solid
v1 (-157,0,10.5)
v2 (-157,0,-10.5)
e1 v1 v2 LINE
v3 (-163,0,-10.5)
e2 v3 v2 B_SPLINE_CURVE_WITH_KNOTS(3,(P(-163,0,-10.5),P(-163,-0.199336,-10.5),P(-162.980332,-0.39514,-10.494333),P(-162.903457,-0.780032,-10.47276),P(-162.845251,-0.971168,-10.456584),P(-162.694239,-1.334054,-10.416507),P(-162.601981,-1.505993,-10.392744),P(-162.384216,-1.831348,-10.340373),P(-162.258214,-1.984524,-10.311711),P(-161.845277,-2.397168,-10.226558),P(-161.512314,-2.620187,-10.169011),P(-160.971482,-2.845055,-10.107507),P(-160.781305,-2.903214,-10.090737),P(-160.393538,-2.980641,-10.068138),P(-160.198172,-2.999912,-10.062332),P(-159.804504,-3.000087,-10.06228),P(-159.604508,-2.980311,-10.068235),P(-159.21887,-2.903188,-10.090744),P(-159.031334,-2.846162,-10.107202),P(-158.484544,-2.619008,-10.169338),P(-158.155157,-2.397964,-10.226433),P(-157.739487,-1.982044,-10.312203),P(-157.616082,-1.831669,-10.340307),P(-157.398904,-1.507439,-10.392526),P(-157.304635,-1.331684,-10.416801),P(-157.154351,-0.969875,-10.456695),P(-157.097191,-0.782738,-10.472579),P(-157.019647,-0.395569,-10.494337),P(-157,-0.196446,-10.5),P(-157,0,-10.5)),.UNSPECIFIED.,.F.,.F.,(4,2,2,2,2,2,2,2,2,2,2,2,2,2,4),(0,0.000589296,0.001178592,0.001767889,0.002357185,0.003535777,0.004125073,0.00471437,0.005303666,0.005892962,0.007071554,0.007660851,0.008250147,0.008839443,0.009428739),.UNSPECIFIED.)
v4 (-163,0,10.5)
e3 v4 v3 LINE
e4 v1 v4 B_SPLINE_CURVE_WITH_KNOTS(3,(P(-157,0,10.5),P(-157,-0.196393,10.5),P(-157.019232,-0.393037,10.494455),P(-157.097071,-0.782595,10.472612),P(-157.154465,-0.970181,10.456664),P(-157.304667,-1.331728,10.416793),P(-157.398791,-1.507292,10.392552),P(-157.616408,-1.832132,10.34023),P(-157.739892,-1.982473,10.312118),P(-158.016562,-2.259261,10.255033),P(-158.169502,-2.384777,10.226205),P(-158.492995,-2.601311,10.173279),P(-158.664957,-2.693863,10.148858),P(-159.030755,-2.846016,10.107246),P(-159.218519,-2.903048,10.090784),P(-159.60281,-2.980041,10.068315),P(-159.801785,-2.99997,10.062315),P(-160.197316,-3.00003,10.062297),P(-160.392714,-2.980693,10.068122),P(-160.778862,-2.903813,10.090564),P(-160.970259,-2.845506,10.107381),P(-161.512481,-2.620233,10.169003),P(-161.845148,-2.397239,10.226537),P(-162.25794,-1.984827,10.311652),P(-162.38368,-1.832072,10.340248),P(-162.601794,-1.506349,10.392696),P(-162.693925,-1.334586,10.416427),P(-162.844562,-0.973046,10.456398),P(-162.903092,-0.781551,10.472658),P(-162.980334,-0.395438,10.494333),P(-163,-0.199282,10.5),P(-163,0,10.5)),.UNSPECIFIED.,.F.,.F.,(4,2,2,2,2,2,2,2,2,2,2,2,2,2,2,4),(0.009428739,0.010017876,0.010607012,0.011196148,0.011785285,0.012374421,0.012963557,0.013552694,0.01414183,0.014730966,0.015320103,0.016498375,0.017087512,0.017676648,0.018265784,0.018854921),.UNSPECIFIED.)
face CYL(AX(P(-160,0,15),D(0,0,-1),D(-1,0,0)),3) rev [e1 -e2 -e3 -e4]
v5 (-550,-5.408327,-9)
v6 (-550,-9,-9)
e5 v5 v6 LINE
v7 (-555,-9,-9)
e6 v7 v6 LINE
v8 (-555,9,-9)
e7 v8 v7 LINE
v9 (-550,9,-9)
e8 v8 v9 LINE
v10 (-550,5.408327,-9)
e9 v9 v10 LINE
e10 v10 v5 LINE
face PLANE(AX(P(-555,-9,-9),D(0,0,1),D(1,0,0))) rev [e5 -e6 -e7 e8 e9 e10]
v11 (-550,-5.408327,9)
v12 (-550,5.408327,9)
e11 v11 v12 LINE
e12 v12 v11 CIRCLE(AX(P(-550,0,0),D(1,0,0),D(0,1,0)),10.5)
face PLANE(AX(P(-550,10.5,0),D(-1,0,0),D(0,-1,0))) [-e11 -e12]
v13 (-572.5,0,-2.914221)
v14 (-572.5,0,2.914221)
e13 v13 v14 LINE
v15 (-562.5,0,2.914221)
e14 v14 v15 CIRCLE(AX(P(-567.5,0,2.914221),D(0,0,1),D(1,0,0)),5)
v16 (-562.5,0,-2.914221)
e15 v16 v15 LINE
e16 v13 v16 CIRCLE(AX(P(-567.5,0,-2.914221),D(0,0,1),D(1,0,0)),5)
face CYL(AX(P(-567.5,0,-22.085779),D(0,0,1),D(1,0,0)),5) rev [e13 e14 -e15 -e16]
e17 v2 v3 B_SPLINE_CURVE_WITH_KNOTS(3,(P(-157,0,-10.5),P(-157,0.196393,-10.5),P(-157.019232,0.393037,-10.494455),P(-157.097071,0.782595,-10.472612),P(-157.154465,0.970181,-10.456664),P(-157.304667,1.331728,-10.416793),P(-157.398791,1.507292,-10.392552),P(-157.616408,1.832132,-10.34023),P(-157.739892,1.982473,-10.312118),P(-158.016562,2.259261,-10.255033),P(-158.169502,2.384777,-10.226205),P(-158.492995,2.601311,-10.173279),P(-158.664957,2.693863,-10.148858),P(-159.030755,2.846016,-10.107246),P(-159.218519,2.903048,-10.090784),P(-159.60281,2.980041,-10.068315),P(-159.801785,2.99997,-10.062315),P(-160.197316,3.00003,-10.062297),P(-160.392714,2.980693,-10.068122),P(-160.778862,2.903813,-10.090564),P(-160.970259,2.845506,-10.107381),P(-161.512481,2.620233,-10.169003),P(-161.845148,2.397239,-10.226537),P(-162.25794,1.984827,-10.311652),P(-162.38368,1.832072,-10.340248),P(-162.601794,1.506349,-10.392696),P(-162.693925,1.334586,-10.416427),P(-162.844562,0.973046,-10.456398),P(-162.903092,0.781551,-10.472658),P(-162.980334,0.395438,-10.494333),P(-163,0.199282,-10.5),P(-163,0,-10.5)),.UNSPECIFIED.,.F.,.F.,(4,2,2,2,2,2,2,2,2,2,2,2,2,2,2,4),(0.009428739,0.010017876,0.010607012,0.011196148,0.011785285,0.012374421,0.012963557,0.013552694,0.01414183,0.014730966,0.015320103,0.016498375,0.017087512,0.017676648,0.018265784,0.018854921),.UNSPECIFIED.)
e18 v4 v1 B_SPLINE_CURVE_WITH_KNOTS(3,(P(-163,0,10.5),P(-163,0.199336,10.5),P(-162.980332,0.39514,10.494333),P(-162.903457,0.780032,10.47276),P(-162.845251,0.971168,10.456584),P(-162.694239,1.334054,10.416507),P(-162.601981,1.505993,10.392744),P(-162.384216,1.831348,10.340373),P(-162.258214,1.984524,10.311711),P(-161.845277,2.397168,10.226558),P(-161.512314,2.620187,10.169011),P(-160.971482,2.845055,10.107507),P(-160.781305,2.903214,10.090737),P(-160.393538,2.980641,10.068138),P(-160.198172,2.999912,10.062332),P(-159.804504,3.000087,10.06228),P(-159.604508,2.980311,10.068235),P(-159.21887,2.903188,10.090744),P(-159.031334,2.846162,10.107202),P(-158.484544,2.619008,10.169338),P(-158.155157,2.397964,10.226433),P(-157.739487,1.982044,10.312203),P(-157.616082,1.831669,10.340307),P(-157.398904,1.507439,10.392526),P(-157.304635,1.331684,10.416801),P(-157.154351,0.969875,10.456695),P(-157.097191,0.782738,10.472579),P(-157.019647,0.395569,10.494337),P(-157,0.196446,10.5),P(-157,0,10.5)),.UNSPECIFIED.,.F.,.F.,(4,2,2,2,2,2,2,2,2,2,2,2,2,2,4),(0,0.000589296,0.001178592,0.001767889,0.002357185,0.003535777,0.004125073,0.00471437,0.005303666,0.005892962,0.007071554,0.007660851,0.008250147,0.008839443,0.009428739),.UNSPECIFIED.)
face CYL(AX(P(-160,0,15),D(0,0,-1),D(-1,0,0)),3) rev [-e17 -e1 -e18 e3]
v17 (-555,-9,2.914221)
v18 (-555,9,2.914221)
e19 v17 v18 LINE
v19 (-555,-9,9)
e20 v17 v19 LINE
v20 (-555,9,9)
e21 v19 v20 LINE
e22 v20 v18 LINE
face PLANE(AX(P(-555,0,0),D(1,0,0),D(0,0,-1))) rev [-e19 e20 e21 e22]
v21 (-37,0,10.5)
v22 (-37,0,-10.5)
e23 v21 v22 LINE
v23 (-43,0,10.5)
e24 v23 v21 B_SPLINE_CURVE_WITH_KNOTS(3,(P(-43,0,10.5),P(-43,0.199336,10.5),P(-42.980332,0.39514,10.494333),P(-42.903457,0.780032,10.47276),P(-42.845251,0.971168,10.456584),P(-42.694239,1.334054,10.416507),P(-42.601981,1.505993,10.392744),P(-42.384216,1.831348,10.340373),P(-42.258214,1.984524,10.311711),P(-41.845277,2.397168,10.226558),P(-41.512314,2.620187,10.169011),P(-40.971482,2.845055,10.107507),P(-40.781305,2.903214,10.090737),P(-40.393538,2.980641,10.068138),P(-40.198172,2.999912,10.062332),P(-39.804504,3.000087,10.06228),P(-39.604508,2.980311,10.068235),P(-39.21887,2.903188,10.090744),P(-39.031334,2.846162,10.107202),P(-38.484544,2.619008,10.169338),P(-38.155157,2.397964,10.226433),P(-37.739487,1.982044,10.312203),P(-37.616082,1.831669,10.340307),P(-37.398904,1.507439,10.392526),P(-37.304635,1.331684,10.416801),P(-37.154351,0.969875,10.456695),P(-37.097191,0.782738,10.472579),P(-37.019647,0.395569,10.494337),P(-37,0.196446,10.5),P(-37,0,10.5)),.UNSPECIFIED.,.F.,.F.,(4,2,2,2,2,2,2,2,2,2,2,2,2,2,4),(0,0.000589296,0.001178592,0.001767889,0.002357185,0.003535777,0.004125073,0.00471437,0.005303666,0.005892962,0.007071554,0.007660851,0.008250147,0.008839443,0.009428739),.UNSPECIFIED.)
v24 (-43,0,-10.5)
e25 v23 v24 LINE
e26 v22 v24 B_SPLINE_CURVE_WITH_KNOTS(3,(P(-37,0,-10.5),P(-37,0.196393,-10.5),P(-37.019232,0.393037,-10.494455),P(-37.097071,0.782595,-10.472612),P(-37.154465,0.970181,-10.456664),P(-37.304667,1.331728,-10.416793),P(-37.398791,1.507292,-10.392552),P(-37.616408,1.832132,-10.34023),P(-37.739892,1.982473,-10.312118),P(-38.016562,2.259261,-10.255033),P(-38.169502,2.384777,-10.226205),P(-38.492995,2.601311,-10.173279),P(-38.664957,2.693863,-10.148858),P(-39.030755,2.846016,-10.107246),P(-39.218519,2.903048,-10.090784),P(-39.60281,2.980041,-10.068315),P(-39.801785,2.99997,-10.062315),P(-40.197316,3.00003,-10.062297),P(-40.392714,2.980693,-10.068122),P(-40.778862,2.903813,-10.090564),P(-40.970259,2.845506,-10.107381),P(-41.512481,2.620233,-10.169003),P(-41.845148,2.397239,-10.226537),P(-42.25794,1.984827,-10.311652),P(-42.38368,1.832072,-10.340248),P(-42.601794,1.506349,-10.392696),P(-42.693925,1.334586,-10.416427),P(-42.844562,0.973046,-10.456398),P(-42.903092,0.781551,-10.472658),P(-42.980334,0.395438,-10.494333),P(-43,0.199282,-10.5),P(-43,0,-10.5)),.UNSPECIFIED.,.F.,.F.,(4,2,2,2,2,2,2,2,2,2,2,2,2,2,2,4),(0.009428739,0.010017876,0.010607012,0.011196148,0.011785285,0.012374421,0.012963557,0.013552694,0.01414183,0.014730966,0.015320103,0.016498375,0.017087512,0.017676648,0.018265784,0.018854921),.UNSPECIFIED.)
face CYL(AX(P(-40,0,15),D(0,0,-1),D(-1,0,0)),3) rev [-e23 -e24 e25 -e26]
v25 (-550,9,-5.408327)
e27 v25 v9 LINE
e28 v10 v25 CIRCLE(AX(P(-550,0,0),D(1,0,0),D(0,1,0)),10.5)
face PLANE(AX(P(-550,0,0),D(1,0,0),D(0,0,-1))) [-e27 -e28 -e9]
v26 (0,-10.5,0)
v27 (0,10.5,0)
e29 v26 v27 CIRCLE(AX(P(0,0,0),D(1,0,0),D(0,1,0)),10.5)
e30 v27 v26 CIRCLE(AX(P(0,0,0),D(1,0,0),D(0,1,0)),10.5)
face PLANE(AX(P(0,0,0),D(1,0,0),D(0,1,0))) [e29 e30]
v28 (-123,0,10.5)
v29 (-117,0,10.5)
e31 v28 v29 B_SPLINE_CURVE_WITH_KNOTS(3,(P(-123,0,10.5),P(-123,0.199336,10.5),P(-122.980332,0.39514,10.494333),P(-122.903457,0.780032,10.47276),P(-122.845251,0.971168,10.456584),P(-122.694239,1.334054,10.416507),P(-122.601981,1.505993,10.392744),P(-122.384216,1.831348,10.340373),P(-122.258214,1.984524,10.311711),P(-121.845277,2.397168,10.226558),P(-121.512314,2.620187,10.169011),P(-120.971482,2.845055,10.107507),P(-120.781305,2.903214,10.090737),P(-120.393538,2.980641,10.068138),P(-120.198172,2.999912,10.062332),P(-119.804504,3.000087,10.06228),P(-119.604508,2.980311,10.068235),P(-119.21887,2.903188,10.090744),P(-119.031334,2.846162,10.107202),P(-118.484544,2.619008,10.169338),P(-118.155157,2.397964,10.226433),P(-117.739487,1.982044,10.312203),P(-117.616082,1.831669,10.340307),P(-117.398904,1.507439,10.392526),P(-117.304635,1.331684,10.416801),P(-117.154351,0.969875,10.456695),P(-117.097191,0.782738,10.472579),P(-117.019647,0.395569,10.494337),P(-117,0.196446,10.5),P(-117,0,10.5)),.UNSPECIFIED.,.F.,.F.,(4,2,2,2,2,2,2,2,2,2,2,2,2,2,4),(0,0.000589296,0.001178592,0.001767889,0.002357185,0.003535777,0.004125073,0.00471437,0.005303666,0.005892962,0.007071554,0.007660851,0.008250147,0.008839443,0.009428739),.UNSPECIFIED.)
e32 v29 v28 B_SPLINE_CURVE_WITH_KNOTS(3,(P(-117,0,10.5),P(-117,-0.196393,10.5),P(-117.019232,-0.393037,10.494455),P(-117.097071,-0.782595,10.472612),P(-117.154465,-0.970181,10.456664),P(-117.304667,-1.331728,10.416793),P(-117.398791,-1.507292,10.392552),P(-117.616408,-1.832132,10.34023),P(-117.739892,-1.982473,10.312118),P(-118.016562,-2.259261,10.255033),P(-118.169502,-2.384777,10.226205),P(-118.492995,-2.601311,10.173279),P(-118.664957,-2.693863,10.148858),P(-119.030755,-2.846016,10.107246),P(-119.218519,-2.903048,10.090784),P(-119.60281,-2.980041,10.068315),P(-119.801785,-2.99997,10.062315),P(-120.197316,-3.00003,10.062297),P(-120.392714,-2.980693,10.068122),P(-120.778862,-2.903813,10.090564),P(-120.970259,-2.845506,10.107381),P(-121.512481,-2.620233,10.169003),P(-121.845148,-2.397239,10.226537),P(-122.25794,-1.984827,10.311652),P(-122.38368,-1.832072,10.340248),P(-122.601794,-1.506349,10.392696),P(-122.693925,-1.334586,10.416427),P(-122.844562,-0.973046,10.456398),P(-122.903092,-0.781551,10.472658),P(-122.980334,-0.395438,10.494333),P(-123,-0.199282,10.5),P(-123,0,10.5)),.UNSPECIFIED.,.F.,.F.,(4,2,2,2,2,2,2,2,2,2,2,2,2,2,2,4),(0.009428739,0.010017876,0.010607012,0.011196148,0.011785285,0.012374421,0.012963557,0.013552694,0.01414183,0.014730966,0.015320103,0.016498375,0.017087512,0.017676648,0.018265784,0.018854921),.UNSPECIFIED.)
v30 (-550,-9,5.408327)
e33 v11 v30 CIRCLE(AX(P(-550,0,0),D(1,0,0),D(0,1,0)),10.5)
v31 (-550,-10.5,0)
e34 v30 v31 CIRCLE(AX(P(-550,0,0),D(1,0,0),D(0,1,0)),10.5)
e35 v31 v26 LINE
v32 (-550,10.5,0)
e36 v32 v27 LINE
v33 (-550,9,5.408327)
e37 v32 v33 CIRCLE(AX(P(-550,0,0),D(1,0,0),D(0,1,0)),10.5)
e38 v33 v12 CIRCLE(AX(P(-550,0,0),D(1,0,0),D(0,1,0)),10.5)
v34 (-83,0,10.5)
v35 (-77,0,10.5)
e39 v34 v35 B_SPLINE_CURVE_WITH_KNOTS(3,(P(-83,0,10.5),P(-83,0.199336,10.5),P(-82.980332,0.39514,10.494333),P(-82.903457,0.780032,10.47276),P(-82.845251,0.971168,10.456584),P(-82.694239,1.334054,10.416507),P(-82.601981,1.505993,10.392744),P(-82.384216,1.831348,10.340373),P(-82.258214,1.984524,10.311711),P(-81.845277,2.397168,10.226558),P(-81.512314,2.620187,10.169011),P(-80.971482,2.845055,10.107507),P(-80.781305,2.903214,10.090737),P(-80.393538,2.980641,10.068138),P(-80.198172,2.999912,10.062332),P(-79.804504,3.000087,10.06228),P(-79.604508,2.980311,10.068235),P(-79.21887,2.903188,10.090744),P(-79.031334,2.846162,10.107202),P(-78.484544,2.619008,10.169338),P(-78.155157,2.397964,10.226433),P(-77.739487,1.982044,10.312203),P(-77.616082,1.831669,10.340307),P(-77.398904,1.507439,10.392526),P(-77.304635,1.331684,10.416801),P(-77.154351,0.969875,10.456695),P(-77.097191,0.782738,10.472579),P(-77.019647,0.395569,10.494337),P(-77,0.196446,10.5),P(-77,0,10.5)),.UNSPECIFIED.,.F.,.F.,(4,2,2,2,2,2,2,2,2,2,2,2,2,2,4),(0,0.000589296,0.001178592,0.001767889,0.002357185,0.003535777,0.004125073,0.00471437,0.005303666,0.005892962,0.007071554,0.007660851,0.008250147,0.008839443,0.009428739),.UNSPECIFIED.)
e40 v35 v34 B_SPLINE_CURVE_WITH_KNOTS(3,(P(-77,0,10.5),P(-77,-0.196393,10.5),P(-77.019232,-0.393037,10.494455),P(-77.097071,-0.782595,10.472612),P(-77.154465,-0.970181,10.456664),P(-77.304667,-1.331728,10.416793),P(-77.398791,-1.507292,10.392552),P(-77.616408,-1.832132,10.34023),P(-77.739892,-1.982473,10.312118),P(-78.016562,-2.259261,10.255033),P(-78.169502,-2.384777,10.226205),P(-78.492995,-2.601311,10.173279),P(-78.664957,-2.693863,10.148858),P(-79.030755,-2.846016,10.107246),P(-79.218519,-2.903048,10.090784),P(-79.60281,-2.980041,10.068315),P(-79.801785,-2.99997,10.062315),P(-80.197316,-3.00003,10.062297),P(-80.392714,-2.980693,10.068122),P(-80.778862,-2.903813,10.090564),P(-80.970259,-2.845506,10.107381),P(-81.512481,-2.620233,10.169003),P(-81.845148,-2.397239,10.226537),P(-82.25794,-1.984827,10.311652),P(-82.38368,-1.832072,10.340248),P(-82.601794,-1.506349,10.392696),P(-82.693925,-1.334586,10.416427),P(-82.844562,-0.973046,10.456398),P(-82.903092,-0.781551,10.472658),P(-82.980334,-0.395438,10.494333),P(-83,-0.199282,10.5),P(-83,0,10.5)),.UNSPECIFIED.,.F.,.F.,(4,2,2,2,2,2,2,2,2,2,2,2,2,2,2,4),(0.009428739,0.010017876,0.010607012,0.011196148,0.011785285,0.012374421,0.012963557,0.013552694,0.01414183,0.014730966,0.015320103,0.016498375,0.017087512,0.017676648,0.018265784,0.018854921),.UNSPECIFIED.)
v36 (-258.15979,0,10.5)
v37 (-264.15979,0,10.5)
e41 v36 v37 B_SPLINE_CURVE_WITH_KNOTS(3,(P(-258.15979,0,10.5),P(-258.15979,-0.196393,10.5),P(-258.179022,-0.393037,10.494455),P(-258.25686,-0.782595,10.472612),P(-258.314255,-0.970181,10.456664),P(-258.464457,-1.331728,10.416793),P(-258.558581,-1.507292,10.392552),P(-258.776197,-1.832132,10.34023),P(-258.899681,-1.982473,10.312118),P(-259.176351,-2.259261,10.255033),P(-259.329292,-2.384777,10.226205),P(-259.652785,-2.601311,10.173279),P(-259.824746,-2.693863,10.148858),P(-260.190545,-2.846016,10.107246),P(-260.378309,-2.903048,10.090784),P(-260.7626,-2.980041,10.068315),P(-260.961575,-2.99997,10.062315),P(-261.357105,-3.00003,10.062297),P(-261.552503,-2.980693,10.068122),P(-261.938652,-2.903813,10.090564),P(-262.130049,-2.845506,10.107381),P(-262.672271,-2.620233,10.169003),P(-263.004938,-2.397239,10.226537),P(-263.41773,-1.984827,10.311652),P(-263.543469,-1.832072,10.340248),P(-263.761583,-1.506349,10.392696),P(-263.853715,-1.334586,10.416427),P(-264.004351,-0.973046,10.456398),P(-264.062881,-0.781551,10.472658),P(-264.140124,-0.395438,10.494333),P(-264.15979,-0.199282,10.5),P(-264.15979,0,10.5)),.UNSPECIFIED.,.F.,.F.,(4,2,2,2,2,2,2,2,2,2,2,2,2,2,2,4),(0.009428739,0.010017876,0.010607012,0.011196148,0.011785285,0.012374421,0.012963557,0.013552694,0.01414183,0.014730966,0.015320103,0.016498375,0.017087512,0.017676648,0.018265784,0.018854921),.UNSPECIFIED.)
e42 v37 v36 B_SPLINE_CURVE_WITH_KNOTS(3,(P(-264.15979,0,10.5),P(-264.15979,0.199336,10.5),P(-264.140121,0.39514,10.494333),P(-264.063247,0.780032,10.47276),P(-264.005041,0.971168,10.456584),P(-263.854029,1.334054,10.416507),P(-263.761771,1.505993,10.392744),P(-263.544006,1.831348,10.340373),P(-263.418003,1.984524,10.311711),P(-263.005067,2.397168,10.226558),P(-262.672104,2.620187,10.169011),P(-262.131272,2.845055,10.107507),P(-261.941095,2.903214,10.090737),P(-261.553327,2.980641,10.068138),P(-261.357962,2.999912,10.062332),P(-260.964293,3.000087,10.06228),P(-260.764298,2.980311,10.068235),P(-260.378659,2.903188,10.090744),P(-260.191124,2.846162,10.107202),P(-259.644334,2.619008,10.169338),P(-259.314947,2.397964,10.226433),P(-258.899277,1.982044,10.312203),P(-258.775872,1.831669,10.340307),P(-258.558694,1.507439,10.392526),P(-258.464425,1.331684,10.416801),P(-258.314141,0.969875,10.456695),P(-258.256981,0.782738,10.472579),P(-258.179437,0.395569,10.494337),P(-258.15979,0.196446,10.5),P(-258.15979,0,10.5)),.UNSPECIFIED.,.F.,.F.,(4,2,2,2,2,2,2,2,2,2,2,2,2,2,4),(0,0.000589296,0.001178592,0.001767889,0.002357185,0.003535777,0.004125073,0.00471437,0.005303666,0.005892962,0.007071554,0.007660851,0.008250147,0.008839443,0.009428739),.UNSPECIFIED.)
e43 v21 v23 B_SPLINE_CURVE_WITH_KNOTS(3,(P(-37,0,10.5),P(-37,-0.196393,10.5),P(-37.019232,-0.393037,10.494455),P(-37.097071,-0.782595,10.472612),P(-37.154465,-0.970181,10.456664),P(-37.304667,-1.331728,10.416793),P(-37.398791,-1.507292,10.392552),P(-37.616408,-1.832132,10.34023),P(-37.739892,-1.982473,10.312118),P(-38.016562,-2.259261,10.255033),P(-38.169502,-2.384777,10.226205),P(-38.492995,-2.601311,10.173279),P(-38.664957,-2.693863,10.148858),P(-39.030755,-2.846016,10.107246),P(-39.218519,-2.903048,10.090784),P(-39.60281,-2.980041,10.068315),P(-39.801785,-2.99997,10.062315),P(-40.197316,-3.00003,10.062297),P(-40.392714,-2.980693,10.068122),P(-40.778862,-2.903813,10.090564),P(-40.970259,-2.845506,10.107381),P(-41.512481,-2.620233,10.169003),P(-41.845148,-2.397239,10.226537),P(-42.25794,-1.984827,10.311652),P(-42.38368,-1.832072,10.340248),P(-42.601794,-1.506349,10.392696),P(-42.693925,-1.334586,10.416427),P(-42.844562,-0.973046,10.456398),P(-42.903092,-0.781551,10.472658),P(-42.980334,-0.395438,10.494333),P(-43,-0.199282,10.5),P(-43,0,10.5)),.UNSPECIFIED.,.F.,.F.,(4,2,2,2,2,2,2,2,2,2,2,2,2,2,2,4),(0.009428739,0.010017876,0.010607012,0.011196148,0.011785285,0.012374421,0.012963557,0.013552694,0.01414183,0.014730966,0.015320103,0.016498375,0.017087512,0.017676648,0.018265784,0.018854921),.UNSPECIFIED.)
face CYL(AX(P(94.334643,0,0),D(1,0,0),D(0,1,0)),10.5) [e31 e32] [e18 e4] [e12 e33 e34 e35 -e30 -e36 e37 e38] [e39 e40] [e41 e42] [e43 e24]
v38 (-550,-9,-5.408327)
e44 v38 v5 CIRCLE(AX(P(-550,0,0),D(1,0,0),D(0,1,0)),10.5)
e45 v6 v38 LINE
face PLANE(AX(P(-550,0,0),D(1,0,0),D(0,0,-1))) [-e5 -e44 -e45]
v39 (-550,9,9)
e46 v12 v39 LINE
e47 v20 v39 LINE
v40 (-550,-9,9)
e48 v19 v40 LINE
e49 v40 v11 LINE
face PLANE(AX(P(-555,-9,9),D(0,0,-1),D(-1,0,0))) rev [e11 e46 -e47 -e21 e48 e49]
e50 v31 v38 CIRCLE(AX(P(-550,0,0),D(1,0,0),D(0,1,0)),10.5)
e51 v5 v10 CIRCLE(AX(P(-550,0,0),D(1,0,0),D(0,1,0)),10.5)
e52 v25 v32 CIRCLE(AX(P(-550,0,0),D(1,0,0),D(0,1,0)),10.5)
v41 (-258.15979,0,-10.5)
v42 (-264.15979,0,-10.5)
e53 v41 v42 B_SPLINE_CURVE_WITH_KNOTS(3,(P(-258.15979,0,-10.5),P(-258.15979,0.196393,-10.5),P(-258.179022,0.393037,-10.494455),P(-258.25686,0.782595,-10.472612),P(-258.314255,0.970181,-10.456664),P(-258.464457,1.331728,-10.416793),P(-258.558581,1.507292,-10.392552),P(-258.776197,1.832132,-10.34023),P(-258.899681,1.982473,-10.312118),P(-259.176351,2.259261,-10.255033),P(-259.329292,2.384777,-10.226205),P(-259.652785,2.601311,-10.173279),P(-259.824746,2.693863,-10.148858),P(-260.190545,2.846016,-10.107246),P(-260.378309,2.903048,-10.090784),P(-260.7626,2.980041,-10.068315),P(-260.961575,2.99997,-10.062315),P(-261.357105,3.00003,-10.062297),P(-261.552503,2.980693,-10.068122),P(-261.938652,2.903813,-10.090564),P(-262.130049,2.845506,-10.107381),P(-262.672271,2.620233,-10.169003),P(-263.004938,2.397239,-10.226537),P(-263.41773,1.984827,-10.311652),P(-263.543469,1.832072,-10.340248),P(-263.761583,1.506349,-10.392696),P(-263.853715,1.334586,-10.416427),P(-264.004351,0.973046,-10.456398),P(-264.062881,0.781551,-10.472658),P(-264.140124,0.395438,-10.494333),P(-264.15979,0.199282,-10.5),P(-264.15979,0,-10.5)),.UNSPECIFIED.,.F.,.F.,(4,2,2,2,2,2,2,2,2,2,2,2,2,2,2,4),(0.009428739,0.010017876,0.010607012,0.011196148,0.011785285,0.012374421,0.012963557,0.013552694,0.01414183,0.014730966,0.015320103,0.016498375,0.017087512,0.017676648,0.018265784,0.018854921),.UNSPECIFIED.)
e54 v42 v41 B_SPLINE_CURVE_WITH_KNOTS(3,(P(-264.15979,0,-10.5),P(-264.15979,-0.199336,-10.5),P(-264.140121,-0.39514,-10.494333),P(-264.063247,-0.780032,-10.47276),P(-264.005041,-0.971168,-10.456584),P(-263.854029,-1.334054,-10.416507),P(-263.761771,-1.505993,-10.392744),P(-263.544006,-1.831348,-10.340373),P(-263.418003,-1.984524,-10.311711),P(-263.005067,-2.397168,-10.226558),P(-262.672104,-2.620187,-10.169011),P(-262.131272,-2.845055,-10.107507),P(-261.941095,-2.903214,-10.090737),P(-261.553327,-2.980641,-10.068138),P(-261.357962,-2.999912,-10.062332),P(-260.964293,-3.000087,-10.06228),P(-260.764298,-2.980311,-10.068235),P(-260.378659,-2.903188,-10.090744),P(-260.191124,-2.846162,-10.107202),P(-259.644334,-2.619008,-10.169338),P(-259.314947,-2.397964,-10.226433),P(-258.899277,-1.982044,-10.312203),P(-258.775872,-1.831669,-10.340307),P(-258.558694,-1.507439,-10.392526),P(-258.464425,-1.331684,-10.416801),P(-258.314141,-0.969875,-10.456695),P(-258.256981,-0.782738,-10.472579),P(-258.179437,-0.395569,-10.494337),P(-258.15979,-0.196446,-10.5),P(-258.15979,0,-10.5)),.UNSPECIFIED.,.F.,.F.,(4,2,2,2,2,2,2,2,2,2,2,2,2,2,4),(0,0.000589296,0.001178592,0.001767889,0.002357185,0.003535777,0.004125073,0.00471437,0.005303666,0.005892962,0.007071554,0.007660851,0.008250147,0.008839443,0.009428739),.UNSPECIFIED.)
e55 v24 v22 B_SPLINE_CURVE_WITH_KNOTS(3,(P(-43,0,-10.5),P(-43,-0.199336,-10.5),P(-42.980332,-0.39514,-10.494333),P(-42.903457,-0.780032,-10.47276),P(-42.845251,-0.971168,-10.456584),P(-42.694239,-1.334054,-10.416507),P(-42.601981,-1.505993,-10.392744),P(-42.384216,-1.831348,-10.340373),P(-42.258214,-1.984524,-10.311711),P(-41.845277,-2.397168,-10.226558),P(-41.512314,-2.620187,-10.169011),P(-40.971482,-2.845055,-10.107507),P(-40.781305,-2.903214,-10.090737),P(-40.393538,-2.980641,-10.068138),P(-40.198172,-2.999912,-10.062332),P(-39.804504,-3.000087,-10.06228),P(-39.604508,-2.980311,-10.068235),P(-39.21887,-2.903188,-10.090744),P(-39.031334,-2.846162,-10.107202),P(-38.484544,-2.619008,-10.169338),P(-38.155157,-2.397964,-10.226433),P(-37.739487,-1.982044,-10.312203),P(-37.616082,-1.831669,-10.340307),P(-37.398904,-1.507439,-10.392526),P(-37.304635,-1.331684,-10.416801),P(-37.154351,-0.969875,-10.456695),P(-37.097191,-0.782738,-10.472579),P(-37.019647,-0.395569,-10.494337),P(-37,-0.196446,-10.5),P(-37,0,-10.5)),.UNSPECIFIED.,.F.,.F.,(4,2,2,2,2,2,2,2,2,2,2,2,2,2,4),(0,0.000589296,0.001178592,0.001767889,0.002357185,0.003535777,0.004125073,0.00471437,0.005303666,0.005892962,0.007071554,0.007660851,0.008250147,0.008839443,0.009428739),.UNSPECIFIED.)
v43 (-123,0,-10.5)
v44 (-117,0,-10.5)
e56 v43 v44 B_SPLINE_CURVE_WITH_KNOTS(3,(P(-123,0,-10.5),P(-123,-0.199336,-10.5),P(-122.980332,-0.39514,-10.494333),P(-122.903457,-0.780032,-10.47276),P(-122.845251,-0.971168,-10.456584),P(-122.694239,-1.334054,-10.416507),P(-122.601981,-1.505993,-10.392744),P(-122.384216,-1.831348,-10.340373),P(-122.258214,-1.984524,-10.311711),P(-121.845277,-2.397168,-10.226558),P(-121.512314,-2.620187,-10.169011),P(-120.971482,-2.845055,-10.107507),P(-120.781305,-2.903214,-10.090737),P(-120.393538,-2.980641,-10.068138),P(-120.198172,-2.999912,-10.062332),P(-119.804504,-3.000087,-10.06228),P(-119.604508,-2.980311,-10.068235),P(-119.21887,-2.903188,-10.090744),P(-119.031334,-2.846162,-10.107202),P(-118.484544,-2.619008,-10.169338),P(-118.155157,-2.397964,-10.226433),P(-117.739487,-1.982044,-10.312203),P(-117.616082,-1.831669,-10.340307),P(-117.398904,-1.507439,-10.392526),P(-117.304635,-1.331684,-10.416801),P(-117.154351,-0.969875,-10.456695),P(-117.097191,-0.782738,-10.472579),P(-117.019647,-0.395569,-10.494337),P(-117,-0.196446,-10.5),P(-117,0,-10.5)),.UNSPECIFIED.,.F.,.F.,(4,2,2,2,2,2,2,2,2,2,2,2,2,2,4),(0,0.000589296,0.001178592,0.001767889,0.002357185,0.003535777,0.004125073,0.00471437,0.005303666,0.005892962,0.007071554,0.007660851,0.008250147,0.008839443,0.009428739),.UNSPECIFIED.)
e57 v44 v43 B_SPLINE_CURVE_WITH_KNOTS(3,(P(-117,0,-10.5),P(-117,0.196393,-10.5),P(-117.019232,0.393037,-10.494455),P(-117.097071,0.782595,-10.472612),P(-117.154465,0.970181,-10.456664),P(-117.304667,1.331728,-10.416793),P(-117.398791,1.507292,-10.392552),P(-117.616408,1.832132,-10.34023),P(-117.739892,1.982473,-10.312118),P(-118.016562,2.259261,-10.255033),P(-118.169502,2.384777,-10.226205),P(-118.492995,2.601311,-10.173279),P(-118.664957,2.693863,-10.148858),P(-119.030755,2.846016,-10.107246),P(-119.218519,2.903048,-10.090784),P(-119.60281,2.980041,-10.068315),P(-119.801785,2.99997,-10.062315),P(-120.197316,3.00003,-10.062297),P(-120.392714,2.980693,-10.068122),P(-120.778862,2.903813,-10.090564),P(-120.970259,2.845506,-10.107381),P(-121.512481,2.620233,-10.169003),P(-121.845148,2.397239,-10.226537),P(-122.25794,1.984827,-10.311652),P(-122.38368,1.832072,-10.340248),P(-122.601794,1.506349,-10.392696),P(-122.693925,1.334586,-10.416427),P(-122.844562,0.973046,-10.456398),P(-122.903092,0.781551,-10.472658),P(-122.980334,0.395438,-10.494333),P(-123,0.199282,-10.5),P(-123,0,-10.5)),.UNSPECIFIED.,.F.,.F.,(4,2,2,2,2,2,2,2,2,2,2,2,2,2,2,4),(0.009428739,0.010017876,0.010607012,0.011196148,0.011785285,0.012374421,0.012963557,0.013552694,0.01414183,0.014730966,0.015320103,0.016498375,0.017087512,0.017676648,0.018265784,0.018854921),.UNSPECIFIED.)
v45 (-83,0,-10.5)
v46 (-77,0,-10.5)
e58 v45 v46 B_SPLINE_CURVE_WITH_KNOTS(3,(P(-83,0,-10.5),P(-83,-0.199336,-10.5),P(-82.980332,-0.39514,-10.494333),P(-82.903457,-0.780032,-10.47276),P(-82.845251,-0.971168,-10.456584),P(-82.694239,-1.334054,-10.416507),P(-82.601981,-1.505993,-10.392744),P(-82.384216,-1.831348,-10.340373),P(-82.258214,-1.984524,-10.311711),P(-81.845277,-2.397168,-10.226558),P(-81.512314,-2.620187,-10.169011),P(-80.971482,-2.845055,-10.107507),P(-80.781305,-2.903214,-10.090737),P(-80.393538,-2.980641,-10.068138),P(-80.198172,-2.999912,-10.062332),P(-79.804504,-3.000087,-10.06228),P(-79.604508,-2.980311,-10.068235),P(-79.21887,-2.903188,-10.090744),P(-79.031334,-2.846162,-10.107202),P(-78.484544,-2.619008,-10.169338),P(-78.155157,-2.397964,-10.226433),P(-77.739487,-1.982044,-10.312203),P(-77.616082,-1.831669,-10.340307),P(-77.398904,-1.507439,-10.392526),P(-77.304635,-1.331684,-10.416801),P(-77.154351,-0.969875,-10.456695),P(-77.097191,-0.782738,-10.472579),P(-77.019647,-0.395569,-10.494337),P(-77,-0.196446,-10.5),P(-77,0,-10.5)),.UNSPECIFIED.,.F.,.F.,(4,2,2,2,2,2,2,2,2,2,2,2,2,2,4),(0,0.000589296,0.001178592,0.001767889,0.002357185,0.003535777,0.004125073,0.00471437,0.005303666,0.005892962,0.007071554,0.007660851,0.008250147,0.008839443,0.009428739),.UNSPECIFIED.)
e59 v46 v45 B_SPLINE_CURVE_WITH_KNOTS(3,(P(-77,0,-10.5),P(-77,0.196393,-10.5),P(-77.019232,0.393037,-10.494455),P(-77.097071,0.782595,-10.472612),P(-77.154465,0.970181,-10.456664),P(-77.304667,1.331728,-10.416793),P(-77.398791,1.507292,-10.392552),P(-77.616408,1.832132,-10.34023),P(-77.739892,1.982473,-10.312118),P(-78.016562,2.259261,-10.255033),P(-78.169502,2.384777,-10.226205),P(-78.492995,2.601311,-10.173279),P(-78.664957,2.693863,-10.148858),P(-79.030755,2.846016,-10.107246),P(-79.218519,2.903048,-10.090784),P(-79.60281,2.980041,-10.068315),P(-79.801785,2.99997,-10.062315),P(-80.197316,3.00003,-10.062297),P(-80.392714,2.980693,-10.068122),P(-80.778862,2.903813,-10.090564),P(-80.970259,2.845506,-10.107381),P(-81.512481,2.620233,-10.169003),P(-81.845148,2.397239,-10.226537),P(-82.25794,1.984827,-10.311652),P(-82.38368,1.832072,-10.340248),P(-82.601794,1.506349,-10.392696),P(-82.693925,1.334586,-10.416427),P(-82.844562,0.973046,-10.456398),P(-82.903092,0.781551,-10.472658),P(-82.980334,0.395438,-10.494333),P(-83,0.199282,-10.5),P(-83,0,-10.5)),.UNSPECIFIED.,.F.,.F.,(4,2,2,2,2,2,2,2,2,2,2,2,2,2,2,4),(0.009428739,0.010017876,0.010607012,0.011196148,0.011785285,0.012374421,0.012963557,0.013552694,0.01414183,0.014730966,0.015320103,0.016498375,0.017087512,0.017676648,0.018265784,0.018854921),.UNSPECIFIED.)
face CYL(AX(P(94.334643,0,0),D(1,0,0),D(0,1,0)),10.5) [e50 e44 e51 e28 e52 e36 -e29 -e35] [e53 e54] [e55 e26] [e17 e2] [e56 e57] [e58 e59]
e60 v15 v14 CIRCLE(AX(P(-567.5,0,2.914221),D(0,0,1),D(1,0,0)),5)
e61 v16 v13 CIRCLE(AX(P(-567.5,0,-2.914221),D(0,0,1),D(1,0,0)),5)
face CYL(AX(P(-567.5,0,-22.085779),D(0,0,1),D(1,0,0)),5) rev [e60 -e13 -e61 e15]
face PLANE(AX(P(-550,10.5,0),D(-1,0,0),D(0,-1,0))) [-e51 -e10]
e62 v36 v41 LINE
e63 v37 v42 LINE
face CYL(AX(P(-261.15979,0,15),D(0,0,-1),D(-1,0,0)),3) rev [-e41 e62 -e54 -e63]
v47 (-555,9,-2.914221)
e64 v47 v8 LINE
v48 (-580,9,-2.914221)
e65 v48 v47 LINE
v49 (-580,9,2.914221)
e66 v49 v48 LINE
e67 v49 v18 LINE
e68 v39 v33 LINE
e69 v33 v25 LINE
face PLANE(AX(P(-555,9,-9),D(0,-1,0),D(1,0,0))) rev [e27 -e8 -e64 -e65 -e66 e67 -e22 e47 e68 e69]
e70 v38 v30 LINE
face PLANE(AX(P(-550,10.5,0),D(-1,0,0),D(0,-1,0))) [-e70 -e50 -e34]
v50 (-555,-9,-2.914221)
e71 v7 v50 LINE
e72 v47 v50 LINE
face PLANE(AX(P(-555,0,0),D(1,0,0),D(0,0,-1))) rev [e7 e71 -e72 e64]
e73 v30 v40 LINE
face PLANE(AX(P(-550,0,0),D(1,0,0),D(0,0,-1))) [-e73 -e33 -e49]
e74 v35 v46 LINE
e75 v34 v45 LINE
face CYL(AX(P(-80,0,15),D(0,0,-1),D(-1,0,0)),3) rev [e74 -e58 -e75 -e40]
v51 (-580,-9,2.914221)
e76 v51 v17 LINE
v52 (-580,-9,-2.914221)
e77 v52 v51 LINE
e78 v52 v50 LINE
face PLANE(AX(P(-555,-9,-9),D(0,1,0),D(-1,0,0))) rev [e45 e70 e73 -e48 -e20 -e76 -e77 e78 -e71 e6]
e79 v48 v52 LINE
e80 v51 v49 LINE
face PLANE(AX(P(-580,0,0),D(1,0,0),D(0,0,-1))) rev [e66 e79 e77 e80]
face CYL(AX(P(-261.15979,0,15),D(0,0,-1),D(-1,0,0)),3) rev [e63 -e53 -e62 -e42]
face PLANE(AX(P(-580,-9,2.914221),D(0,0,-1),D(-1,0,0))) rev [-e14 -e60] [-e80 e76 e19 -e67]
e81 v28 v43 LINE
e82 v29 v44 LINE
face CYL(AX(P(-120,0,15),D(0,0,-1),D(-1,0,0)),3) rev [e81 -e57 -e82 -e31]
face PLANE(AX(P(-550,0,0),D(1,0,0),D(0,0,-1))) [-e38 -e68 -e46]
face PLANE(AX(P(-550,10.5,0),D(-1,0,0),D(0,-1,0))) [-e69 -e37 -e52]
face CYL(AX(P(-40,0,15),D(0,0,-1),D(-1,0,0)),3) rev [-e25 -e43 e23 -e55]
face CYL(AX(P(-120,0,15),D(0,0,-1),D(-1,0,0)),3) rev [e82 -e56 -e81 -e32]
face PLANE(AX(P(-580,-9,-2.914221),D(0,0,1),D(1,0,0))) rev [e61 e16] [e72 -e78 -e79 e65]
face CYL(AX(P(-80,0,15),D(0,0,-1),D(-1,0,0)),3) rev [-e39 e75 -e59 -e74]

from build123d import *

# Parameters (mm, degrees)
SKETCH_1_W               = 550
SKETCH_1_H               = 10.5
CUT_EXTRUDE_1_DEPTH      = 15
CUT_EXTRUDE_1_DEPTH_BACK = 15
SKETCH_2_R               = 3
SKETCH_10_W              = 18
SKETCH_10_H              = 18
EXTRUDE_3_DEPTH          = 5
SKETCH_11_W              = 5.828442308
SKETCH_11_H              = 18
EXTRUDE_4_DEPTH          = 25
SKETCH_12_R              = 5
CUT_EXTRUDE_2_DEPTH      = 25


with BuildPart() as part:
    # 草图1 → 旋转1 (revolve)
    with BuildSketch(Plane.XY):
        with Locations((-275, 5.25)):
            Rectangle(SKETCH_1_W, SKETCH_1_H)
    revolve(axis=Axis((94.334642974, 0, 0), (-1, 0, 0)))

    # 草图2 → 切除-拉伸1 (cut, two sides: drawn at the far end of the back side and taken through both)
    with BuildSketch(Plane.XY.offset(-CUT_EXTRUDE_1_DEPTH_BACK)):
        with Locations(Location((-40, 0, 0), (0, 0, 180))):
            Circle(SKETCH_2_R)
        with Locations(Location((-80, 0, 0), (0, 0, 180))):
            Circle(SKETCH_2_R)
        with Locations(Location((-120, 0, 0), (0, 0, 180))):
            Circle(SKETCH_2_R)
        with Locations(Location((-160, 0, 0), (0, 0, 180))):
            Circle(SKETCH_2_R)
        with Locations(Location((-261.159789745, 0, 0), (0, 0, 180))):
            Circle(SKETCH_2_R)
    extrude(amount=CUT_EXTRUDE_1_DEPTH + CUT_EXTRUDE_1_DEPTH_BACK, mode=Mode.SUBTRACT)

    # 草图10 → 凸台-拉伸3 (add)
    with BuildSketch(Plane.ZY.offset(550)):
        Rectangle(SKETCH_10_W, SKETCH_10_H)
    extrude(amount=EXTRUDE_3_DEPTH)

    # 草图11 → 凸台-拉伸4 (add)
    with BuildSketch(Plane.ZY.offset(555)):
        Rectangle(SKETCH_11_W, SKETCH_11_H)
    extrude(amount=EXTRUDE_4_DEPTH)

    # 草图12 → 切除-拉伸2 (cut)
    with BuildSketch(Plane.XY.offset(2.914221154)):
        with Locations((-567.5, 0)):
            Circle(SKETCH_12_R)
    extrude(amount=-CUT_EXTRUDE_2_DEPTH, mode=Mode.SUBTRACT)


solid = part.part
